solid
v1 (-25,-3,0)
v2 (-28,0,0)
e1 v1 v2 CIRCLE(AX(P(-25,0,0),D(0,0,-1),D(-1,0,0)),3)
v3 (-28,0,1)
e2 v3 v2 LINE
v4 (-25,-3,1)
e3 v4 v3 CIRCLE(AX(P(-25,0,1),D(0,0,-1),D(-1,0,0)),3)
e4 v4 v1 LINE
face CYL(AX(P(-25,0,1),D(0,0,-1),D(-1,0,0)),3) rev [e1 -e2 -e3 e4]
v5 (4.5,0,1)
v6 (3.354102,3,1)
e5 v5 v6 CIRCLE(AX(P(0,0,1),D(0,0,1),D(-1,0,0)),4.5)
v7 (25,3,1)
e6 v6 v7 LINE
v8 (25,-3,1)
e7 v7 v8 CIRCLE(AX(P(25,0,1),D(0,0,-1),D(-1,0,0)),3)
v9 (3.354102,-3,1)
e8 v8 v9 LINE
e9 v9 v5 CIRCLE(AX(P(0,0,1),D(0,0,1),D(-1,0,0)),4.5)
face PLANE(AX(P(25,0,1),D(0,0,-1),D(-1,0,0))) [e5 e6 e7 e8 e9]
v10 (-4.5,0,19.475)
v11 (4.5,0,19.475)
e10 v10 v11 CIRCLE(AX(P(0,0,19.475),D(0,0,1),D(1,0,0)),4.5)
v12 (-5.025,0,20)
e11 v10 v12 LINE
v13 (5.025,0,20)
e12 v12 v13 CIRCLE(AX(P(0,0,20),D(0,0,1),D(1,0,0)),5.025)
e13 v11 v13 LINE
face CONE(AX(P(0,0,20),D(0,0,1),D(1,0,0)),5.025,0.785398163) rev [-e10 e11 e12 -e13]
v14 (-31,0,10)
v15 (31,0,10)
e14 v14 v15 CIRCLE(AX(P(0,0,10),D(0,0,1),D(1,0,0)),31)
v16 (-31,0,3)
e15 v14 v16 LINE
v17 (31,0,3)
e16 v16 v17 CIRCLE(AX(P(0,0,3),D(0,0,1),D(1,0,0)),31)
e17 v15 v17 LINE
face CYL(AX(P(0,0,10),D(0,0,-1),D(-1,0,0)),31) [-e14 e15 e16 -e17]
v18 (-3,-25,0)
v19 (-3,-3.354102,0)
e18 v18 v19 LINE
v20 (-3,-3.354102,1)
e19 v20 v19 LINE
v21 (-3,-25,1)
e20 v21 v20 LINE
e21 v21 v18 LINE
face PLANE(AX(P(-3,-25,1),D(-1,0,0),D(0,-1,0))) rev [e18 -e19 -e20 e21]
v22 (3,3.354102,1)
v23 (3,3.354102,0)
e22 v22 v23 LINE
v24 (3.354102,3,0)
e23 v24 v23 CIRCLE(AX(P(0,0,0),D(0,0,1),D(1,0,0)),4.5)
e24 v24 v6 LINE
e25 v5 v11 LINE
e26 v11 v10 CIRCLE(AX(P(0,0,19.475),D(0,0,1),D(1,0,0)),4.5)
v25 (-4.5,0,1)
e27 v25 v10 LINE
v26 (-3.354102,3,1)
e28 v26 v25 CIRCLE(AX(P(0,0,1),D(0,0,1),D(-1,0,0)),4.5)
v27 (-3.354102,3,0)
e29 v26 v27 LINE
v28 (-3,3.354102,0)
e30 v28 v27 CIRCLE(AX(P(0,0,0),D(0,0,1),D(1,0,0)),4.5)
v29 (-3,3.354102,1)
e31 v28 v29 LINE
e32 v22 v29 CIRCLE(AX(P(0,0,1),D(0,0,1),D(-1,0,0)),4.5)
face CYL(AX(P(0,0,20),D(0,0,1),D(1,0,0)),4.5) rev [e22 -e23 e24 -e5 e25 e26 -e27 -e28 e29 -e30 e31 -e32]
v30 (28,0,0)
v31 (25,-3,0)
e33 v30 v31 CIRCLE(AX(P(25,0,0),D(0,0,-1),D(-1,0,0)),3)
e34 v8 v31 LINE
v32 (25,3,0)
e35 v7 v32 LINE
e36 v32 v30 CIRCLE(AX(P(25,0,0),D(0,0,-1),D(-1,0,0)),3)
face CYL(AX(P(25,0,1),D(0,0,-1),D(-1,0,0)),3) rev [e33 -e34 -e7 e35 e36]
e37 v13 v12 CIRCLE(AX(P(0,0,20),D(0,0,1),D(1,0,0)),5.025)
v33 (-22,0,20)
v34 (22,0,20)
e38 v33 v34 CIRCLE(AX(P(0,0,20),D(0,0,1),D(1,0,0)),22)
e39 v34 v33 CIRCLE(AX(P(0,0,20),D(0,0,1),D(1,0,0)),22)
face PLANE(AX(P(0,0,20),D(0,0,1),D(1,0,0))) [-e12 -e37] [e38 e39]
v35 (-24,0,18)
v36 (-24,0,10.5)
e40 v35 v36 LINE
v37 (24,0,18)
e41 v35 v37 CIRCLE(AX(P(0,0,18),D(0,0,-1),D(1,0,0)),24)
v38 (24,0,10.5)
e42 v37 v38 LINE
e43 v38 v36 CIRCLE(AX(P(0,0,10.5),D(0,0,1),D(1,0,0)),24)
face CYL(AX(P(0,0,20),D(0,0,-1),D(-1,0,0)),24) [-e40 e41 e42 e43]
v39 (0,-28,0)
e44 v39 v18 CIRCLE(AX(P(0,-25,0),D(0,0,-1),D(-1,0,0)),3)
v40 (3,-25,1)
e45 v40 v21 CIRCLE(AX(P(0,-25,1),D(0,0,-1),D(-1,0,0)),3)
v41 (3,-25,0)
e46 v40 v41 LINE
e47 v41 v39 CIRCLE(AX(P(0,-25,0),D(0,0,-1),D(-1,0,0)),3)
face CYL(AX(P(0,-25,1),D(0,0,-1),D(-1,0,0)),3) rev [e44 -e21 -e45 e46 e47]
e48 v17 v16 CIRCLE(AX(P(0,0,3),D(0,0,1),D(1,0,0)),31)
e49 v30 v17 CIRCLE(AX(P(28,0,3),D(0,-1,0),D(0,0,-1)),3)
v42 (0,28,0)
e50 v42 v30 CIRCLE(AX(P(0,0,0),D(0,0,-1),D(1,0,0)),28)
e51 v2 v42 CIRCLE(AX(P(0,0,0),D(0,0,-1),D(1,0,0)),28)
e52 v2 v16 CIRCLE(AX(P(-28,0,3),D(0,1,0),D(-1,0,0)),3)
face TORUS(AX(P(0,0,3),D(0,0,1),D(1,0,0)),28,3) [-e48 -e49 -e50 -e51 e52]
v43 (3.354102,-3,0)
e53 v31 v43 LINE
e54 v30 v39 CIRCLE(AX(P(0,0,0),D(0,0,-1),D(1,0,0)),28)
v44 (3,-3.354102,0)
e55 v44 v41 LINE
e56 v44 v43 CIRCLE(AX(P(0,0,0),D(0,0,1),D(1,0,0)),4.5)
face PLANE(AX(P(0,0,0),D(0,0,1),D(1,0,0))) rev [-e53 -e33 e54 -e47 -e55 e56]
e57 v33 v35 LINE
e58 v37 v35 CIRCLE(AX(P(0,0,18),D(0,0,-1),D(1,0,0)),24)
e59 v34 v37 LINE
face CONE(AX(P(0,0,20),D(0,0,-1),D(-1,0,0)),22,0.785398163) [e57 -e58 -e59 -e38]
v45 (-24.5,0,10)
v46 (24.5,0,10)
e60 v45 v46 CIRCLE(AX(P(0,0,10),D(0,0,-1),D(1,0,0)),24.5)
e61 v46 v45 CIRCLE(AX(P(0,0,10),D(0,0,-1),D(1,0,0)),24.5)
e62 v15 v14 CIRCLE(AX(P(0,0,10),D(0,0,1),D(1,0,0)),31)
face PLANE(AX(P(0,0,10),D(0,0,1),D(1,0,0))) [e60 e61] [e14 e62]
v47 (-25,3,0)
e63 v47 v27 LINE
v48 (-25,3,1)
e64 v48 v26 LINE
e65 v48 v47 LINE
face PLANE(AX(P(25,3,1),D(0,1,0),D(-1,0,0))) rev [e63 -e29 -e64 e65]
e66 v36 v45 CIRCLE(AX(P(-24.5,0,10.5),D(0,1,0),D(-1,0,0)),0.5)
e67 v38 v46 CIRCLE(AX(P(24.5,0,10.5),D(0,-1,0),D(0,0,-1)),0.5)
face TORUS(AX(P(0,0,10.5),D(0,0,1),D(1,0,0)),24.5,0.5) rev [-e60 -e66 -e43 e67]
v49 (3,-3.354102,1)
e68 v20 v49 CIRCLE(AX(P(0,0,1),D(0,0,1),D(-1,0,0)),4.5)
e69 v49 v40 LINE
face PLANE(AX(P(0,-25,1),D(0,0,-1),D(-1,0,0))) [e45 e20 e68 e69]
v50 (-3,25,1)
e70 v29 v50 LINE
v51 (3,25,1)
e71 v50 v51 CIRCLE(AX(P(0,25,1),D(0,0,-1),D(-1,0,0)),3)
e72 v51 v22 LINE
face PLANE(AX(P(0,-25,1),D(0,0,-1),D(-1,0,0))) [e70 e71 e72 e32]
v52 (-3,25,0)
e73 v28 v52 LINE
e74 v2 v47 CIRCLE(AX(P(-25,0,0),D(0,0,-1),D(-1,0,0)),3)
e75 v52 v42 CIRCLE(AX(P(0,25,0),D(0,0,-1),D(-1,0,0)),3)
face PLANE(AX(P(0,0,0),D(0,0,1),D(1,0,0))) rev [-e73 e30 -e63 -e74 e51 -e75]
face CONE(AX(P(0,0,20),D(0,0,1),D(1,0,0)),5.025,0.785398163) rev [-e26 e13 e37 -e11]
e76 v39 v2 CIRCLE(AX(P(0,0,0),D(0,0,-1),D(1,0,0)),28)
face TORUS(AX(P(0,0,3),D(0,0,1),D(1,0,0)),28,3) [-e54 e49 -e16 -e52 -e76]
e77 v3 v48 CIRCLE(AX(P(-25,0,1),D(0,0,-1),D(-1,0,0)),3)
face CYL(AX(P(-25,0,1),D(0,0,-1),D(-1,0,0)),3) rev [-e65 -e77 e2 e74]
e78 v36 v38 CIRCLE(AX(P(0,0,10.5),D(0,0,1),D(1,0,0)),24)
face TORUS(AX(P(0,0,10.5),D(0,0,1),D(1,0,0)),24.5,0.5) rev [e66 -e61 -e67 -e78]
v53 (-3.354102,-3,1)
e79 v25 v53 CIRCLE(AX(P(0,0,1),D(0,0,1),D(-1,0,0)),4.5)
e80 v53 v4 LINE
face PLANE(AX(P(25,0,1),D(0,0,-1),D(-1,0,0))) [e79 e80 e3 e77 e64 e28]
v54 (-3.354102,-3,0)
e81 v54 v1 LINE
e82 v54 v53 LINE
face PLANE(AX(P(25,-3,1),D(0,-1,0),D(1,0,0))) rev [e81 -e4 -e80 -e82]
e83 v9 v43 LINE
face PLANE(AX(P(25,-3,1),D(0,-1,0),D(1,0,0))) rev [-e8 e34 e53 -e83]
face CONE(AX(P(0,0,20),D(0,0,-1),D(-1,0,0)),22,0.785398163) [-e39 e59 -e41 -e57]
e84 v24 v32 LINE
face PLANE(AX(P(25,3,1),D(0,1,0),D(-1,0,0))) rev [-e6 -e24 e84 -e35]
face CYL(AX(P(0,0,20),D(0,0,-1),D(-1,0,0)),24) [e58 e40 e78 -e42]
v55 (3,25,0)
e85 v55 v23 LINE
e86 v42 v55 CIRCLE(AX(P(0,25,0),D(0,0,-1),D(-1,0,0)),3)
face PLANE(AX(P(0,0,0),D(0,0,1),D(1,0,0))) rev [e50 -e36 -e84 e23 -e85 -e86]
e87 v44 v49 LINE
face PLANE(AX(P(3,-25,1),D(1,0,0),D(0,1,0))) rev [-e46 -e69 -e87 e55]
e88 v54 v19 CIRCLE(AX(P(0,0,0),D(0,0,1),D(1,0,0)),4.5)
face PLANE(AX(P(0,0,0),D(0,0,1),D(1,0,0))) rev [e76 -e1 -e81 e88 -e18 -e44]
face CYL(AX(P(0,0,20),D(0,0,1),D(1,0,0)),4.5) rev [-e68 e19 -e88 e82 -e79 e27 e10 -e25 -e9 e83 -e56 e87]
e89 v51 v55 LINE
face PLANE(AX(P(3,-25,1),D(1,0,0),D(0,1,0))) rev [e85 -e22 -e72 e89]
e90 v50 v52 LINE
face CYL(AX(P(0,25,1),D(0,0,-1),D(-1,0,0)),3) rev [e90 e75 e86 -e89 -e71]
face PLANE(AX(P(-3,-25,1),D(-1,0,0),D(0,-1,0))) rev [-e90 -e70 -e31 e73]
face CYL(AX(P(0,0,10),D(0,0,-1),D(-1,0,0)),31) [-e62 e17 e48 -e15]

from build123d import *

# Parameters (mm, degrees)
SKETCH_1_R            = 31
EXTRUDE_1_DEPTH       = 10
SKETCH_2_R            = 24
EXTRUDE_2_DEPTH       = 10
CHAMFER_1_SIZE        = 2
FILLET_1_R            = 3
M10X1_0_1_D           = 9
M10X1_0_1_DEPTH       = 25
M10X1_0_1_CSINK_D     = 10.05
M10X1_0_1_CSINK_ANGLE = 90
M10X1_0_1_TIP         = 2.703872786
CUT_EXTRUDE_1_DEPTH   = 1
CUT_EXTRUDE_2_DEPTH   = 1
FILLET_2_R            = 0.5


with BuildPart() as part:
    # 草图1 → 凸台-拉伸1 (new body)
    with BuildSketch(Plane.XY):
        Circle(SKETCH_1_R)
    extrude(amount=EXTRUDE_1_DEPTH)

    # 草图2 → 凸台-拉伸2 (add)
    with BuildSketch(Plane.XY.offset(10)):
        Circle(SKETCH_2_R)
    extrude(amount=EXTRUDE_2_DEPTH)

    # 倒角1
    chamfer_1_edges = [part.edges().sort_by_distance(p)[0] for p in [
        (-24, 0, 20),
    ]]
    chamfer(chamfer_1_edges, length=CHAMFER_1_SIZE)

    # 圆角1
    fillet_1_edges = [part.edges().sort_by_distance(p)[0] for p in [
        (-31, 0, 0),
    ]]
    fillet(fillet_1_edges, radius=FILLET_1_R)

    # M10x1.0 螺纹孔1
    with Locations(Plane.XY.offset(20)):
        with Locations((0, 0)):
            CounterSinkHole(M10X1_0_1_D / 2, M10X1_0_1_CSINK_D / 2, depth=M10X1_0_1_DEPTH, counter_sink_angle=M10X1_0_1_CSINK_ANGLE)
            with Locations((0, 0, -(M10X1_0_1_DEPTH + M10X1_0_1_TIP / 2))):  # 118° drill point
                Cone(0, M10X1_0_1_D / 2, M10X1_0_1_TIP, mode=Mode.SUBTRACT)

    # 草图4 → 切除-拉伸1 (cut)
    with BuildSketch(Plane(origin=(0, 0, 0), x_dir=(-1, 0, 0), z_dir=(0, 0, -1))):
        with BuildLine():
            Line((-3, -25), (-3, 25))
            ThreePointArc((-3, 25), (0, 28), (3, 25))
            Line((3, 25), (3, -25))
            ThreePointArc((3, -25), (0, -28), (-3, -25))
        make_face()
    extrude(amount=-CUT_EXTRUDE_1_DEPTH, mode=Mode.SUBTRACT)

    # 草图5 → 切除-拉伸2 (cut)
    with BuildSketch(Plane(origin=(0, 0, 0), x_dir=(-1, 0, 0), z_dir=(0, 0, -1))):
        with BuildLine():
            Line((-25, 3), (25, 3))
            ThreePointArc((25, 3), (28, 0), (25, -3))
            Line((25, -3), (-25, -3))
            ThreePointArc((-25, -3), (-28, 0), (-25, 3))
        make_face()
    extrude(amount=-CUT_EXTRUDE_2_DEPTH, mode=Mode.SUBTRACT)

    # 圆角2
    fillet_2_edges = [part.edges().sort_by_distance(p)[0] for p in [
        (-24, 0, 10),
    ]]
    fillet(fillet_2_edges, radius=FILLET_2_R)


solid = part.part
